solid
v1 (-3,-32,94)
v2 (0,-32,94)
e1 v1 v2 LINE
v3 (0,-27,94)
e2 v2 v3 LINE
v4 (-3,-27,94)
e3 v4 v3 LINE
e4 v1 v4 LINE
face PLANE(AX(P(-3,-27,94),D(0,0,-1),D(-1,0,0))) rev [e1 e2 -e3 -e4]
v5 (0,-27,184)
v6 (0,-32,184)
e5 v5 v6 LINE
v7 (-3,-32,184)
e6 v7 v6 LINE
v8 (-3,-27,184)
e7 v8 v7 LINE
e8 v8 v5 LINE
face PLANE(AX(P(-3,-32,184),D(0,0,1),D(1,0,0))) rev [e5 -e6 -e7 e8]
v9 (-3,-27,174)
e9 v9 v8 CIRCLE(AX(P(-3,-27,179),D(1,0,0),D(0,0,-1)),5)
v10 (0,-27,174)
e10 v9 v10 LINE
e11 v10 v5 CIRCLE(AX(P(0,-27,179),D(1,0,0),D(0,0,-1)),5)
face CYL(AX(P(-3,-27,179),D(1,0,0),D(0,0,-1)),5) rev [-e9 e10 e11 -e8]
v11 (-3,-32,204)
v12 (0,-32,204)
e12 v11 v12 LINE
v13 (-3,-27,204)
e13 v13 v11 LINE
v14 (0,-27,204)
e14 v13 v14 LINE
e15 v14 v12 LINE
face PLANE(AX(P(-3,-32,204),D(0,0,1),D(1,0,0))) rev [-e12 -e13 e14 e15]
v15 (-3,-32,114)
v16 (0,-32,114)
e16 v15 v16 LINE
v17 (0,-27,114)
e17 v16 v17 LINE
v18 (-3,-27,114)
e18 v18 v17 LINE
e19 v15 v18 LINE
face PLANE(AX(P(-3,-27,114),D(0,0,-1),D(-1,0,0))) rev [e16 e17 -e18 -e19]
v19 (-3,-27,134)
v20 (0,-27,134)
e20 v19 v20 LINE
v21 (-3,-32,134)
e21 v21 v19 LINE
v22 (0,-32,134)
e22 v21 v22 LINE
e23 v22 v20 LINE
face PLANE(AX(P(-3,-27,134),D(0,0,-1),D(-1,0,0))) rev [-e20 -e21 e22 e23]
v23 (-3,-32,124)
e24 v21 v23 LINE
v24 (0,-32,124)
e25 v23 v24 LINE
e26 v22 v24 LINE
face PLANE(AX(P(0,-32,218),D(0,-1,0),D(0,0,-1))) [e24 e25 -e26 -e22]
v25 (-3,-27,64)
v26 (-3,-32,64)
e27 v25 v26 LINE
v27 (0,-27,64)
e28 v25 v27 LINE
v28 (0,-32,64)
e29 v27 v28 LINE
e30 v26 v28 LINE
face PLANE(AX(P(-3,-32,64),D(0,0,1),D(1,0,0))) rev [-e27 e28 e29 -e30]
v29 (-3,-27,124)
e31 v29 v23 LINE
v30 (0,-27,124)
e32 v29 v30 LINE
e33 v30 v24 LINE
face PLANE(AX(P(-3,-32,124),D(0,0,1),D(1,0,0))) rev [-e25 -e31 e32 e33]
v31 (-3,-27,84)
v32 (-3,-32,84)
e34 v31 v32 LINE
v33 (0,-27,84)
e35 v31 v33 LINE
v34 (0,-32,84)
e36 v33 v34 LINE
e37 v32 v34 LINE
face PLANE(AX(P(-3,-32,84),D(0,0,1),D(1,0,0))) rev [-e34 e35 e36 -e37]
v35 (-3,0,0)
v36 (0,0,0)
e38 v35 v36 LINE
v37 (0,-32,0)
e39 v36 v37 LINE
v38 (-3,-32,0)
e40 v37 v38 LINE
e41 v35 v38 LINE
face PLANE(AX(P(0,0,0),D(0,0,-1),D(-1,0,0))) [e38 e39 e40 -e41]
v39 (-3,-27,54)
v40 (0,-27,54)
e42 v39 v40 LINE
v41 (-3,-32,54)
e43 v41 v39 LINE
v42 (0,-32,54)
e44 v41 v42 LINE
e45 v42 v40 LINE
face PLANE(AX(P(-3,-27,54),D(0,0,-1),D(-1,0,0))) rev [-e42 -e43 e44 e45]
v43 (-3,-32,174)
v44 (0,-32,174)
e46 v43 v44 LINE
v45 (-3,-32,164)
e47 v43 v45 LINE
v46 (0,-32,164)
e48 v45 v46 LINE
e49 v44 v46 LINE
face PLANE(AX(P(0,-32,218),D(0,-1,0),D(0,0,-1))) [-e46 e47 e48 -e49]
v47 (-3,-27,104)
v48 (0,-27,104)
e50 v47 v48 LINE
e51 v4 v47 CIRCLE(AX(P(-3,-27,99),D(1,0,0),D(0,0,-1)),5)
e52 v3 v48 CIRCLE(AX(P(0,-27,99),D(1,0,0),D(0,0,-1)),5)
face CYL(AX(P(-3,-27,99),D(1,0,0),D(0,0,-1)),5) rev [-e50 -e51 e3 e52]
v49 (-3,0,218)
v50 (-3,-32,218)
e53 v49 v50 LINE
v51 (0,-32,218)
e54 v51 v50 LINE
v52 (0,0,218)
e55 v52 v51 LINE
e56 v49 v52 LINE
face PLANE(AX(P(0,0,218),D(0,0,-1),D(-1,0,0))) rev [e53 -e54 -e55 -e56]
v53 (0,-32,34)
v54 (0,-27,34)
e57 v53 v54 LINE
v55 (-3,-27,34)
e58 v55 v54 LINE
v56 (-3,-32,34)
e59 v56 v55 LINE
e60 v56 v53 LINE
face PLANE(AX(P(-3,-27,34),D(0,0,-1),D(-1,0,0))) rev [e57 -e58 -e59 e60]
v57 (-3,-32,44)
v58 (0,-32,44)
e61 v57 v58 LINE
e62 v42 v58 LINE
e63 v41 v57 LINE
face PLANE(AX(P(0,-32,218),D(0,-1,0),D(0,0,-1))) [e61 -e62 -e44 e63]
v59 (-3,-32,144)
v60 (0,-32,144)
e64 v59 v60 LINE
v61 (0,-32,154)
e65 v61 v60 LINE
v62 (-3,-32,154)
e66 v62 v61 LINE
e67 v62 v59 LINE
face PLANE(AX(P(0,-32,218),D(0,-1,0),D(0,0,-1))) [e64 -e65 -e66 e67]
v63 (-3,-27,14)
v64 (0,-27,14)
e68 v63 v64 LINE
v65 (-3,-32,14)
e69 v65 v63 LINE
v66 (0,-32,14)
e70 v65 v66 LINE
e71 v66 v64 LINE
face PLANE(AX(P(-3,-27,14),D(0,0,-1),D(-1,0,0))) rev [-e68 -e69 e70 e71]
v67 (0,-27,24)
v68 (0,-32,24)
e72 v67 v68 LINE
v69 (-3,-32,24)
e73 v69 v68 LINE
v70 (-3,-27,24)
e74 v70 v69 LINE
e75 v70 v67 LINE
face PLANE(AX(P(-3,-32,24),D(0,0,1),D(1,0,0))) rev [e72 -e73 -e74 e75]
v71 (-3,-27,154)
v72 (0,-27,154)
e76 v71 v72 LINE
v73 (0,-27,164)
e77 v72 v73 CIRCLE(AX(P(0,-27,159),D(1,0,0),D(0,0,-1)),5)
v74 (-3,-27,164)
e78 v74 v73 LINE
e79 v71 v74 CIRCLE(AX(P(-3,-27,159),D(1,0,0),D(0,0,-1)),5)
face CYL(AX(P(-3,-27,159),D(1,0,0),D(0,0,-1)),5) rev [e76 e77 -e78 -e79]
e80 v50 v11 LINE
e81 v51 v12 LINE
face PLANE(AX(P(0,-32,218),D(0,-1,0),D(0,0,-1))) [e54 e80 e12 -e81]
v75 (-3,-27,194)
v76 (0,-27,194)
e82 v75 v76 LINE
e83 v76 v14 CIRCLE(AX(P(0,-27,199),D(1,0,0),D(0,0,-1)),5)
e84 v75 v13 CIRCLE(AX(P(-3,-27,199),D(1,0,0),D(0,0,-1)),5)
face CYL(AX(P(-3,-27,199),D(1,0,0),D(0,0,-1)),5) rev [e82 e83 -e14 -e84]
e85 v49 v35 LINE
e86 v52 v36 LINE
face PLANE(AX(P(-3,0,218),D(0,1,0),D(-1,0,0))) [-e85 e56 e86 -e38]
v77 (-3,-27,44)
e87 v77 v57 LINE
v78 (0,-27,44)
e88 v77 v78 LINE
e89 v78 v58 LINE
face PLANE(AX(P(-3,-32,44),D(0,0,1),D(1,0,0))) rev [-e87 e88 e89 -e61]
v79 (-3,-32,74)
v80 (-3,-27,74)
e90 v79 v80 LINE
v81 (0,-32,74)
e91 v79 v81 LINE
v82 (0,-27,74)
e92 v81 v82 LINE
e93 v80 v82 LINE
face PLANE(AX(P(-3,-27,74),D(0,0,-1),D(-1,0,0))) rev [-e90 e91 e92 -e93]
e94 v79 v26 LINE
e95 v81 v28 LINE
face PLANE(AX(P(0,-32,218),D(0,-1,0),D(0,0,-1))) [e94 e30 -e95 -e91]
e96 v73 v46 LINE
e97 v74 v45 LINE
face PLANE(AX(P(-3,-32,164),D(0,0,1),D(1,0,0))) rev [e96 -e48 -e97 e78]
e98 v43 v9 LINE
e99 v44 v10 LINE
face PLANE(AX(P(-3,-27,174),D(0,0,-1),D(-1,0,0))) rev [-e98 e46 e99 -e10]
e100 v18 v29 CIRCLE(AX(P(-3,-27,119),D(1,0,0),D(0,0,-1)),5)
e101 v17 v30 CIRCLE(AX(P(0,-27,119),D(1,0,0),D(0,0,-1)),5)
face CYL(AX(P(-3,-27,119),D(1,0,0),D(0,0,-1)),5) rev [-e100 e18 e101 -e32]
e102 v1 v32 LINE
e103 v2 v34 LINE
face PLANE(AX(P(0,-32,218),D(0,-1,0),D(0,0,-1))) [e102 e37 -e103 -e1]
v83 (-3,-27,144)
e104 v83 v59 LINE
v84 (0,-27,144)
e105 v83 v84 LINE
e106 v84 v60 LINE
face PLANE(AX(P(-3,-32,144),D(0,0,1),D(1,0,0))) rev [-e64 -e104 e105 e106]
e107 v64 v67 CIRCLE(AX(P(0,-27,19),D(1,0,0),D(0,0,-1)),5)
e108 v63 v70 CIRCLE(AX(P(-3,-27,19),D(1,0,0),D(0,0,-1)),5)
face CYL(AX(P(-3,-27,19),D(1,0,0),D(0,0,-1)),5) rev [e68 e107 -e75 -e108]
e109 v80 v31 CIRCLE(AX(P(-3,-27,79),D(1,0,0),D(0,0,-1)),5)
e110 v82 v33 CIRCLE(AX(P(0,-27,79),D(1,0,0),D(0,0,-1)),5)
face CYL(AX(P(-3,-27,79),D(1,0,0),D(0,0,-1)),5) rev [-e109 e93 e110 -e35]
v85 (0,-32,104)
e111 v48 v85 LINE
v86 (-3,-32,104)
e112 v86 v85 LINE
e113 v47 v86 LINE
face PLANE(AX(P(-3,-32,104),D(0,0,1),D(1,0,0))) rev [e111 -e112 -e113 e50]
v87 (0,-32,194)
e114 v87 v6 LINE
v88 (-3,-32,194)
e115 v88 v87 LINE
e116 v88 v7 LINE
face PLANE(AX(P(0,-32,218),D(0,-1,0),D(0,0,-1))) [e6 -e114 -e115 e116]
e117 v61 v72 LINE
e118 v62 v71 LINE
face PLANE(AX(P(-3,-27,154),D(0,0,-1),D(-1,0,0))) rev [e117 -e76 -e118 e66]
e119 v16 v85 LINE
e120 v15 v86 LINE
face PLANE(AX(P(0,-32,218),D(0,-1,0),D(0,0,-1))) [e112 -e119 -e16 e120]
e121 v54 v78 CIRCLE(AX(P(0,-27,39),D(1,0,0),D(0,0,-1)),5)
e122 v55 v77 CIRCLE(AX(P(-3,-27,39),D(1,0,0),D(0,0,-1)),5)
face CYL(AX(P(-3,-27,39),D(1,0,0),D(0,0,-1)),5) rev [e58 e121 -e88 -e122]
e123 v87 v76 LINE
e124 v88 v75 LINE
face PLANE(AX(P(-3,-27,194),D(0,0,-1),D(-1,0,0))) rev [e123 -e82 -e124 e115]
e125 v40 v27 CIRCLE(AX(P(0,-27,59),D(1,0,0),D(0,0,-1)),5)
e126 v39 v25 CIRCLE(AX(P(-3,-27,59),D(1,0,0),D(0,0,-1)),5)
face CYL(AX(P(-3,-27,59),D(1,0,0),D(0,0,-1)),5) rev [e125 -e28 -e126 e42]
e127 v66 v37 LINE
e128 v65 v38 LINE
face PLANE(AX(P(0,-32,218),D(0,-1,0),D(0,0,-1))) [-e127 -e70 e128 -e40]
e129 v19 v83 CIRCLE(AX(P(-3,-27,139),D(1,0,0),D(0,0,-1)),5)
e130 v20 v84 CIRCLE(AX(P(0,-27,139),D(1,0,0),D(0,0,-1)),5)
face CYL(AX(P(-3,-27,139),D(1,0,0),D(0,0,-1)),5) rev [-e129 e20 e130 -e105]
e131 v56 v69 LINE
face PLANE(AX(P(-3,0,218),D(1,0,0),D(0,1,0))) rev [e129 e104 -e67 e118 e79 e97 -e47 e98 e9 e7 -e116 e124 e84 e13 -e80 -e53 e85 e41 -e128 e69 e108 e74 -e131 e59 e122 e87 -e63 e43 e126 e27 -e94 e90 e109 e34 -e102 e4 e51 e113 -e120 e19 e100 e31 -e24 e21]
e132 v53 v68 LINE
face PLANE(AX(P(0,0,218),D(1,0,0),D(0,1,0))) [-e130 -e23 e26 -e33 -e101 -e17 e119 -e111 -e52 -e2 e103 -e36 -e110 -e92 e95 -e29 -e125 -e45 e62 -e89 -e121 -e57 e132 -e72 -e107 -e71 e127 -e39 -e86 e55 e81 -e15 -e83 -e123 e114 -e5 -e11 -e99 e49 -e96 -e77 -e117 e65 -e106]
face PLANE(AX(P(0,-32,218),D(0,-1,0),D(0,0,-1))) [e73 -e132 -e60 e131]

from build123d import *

# Parameters (mm, degrees)
SKETCH1_W           = 3
SKETCH1_H           = 32
EXTRUDE_THIN1_DEPTH = 218
CUT_EXTRUDE1_DEPTH  = 221.356529288
LPATTERN1_COUNT     = 10
LPATTERN1_PITCH     = 20


with BuildPart() as part:
    # Sketch1 → Extrude-Thin1 (new body)
    with BuildSketch(Plane.XY):
        with Locations((-1.5, -16)):
            Rectangle(SKETCH1_W, SKETCH1_H)
    extrude(amount=EXTRUDE_THIN1_DEPTH)

    # Sketch2 → Cut-Extrude1 (cut, through all)
    with BuildSketch(Plane(origin=(0, 0, 0), x_dir=(0, 0, -1), z_dir=(1, 0, 0))):
        with BuildLine():
            Line((-194, -27), (-194, -32))
            Line((-194, -32), (-204, -32))
            Line((-204, -32), (-204, -27))
            ThreePointArc((-204, -27), (-199, -22), (-194, -27))
        make_face()
    cut_extrude1 = extrude(amount=-CUT_EXTRUDE1_DEPTH, mode=Mode.SUBTRACT)

    # LPattern1: Cut-Extrude1 ×10
    with Locations(*[(0, 0, -i * LPATTERN1_PITCH) for i in range(1, LPATTERN1_COUNT)]):
        add(cut_extrude1, mode=Mode.SUBTRACT)


solid = part.part
